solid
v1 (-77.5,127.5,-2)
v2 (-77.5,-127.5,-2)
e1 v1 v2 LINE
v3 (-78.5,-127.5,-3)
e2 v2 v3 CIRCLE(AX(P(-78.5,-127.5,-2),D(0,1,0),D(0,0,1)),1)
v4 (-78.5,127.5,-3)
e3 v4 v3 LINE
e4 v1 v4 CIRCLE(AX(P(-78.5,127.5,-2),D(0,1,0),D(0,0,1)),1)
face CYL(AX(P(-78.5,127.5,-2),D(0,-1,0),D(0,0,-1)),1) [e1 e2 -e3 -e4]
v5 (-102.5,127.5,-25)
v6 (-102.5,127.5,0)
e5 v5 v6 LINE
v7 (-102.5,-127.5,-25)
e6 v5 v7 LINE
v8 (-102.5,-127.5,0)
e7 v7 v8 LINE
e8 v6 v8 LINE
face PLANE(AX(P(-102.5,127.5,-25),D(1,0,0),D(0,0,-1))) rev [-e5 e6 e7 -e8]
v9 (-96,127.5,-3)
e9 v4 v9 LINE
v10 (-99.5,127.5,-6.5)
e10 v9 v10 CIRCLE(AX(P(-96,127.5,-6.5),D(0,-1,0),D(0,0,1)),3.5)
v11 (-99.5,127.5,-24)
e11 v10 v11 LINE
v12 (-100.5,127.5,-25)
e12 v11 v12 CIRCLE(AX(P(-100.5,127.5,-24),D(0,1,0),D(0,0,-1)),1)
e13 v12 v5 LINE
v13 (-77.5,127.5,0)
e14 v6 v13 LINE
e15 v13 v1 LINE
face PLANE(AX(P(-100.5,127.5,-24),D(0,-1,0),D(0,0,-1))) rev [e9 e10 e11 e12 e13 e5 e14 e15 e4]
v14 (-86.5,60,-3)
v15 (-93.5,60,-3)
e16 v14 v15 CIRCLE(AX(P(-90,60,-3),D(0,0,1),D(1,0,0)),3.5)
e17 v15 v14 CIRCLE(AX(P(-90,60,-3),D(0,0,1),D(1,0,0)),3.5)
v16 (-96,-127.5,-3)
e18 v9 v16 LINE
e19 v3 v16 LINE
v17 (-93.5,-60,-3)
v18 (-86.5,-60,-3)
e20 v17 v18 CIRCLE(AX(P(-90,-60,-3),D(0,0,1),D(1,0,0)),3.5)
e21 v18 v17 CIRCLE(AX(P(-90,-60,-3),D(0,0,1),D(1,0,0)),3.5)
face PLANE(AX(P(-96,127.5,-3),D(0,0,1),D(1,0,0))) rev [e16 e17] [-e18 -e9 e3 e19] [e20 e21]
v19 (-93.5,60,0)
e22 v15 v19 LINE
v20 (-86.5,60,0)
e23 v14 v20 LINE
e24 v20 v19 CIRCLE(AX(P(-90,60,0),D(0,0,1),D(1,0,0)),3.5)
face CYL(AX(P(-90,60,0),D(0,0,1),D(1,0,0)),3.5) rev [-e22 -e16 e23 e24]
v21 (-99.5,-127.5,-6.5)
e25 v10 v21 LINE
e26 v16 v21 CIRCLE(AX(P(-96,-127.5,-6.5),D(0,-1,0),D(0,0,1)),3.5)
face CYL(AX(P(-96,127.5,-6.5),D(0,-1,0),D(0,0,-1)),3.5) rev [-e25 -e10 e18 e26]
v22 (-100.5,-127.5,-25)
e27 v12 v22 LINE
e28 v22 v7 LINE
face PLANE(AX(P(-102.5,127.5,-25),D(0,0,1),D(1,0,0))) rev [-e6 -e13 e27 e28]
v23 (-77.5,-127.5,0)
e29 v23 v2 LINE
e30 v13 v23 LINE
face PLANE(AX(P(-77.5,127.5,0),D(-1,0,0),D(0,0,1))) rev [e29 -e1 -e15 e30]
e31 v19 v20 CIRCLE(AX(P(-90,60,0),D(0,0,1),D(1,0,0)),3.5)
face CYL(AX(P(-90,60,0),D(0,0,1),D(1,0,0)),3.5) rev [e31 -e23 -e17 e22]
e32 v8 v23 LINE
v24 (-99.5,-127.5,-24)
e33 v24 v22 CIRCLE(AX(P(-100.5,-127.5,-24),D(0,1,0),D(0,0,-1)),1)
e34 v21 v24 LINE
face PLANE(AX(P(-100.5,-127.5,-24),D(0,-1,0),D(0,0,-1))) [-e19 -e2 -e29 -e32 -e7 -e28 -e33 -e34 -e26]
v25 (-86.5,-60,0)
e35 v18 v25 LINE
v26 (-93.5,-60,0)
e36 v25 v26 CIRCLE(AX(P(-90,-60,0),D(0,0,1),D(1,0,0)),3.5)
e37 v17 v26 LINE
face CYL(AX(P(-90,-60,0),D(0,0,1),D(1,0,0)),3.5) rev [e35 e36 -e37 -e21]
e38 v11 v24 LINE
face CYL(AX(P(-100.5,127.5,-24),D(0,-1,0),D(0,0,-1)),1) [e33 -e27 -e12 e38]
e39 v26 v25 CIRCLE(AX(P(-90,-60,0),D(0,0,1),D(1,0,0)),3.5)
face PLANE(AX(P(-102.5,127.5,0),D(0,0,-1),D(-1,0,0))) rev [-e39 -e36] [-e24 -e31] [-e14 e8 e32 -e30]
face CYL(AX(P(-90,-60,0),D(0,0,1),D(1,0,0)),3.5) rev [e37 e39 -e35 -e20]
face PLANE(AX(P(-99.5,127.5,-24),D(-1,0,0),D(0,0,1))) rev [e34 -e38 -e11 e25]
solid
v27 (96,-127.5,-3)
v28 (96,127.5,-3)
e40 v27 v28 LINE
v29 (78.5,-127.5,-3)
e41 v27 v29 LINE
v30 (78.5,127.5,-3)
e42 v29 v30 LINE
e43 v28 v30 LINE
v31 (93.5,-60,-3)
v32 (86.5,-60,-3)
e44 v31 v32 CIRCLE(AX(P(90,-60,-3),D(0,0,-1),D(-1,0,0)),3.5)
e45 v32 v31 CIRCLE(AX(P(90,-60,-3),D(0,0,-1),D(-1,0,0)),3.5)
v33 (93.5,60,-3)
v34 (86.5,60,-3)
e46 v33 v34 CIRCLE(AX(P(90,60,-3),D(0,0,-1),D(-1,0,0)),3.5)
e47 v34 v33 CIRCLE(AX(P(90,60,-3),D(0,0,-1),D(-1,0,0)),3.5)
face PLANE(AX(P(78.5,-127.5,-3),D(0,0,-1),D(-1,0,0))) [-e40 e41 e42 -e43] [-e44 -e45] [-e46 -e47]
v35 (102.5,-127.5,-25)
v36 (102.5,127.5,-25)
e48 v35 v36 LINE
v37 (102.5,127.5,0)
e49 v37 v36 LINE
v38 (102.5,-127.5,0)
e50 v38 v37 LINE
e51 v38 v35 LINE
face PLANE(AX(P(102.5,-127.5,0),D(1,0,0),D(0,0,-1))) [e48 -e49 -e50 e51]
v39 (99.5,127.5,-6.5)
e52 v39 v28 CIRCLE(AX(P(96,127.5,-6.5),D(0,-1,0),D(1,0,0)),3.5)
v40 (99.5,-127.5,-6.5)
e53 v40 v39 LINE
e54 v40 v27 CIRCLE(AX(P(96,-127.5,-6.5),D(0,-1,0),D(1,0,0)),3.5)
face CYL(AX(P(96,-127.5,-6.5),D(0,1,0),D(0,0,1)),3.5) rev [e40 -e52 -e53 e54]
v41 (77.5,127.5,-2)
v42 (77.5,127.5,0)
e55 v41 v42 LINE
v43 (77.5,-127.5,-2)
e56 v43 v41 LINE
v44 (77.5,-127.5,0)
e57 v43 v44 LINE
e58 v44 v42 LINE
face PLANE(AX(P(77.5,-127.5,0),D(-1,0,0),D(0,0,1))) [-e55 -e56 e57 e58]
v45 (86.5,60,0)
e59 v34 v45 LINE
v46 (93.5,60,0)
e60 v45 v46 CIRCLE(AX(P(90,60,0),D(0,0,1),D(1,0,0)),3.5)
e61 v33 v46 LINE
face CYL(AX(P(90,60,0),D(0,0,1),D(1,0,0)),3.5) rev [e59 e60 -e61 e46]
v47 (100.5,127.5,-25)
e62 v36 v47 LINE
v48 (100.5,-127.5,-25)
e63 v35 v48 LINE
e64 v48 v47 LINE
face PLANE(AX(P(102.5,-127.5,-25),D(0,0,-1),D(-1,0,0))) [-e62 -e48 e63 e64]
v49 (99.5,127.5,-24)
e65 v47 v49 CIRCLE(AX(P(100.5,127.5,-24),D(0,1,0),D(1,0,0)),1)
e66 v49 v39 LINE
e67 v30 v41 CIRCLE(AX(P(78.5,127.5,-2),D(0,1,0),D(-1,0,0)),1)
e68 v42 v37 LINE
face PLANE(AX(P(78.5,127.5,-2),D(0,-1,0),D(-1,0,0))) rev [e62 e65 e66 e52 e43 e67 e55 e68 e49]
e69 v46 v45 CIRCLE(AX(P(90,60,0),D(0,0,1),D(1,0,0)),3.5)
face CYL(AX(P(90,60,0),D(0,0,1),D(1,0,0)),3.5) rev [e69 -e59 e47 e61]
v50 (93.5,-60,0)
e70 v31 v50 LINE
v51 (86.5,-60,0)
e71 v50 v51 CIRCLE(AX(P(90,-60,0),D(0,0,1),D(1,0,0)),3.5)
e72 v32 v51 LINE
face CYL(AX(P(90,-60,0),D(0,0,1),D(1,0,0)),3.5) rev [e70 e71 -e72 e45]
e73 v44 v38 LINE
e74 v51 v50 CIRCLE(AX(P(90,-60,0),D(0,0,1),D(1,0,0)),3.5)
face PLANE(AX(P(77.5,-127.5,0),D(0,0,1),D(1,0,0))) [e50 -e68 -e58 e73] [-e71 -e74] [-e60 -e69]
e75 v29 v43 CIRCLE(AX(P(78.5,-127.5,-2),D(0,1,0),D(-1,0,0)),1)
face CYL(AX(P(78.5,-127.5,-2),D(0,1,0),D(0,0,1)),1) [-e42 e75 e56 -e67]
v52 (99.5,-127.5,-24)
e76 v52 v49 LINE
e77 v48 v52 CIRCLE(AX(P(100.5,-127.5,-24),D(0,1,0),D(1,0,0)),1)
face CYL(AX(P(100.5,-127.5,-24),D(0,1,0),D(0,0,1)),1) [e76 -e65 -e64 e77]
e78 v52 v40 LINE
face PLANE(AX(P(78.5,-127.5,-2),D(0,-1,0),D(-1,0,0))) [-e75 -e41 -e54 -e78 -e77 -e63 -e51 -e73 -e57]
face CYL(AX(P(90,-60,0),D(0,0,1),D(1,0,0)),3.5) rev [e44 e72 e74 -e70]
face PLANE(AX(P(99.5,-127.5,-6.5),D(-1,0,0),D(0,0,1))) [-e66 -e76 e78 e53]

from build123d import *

# Parameters (mm, degrees)
EQUAL_ANGLE_2_5X3_1_DEPTH     = 255
EQUAL_ANGLE_2_5X3_1_2_DEPTH   = 255
M6_CLEARANCE_HOLE1_AT_2_COUNT = 2
M6_CLEARANCE_HOLE1_AT_2_PITCH = 120
M6_CLEARANCE_HOLE1_AT_3_COUNT = 2
M6_CLEARANCE_HOLE1_AT_3_PITCH = 216.333076528
M6_CLEARANCE_HOLE1_AT_4_COUNT = 2
M6_CLEARANCE_HOLE1_AT_4_PITCH = 180


with BuildPart() as part:
    # Sketch1 → Equal Angle 2.5X3(1) (new body)
    with BuildSketch(Plane(origin=(-102.5, -127.5, 0), x_dir=(0, 0, -1), z_dir=(0, 1, 0))):
        with BuildLine():
            Line((25, 0), (0, 0))
            Line((0, 0), (0, -25))
            Line((0, -25), (2, -25))
            ThreePointArc((2, -25), (2.707106781, -24.707106781), (3, -24))
            Line((3, -24), (3, -6.5))
            ThreePointArc((3, -6.5), (4.025126266, -4.025126266), (6.5, -3))
            Line((6.5, -3), (24, -3))
            ThreePointArc((24, -3), (24.707106781, -2.707106781), (25, -2))
            Line((25, -2), (25, 0))
        make_face()
    extrude(amount=EQUAL_ANGLE_2_5X3_1_DEPTH)

    # Sketch6 → M6 Clearance Hole1 (revolve, cut)
    with BuildSketch(Plane(origin=(-90, 60, 0), x_dir=(0, -1, 0), z_dir=(1, 0, 0))):
        Polygon((0, 0), (0, 22.103012167), (3.5, 20), (3.5, 0), align=None)
    m6_clearance_hole1 = revolve(axis=Axis((-90, 60, 6.35), (0, 0, -1)), mode=Mode.SUBTRACT)

    # M6 Clearance Hole1 at 2: M6 Clearance Hole1 ×2
    with Locations(*[(0, -i * M6_CLEARANCE_HOLE1_AT_2_PITCH, 0) for i in range(1, M6_CLEARANCE_HOLE1_AT_2_COUNT)]):
        add(m6_clearance_hole1, mode=Mode.SUBTRACT)


with BuildPart() as body_2:
    # Sketch1 on segment 2 (carried to segment 2) → Equal Angle 2.5X3_1 2 (new body)
    with BuildSketch(Plane(origin=(102.5, -127.5, 0), x_dir=(-1, 0, 0), z_dir=(0, 1, 0))):
        with BuildLine():
            Line((25, 0), (0, 0))
            Line((0, 0), (0, -25))
            Line((0, -25), (2, -25))
            ThreePointArc((2, -25), (2.707106781, -24.707106781), (3, -24))
            Line((3, -24), (3, -6.5))
            ThreePointArc((3, -6.5), (4.025126266, -4.025126266), (6.5, -3))
            Line((6.5, -3), (24, -3))
            ThreePointArc((24, -3), (24.707106781, -2.707106781), (25, -2))
            Line((25, -2), (25, 0))
        make_face()
    extrude(amount=EQUAL_ANGLE_2_5X3_1_2_DEPTH)

    # M6 Clearance Hole1 at 3: M6 Clearance Hole1 ×2
    with Locations(*[Vector(0.8320502943378437, -0.5547001962252293, 0) * (i * M6_CLEARANCE_HOLE1_AT_3_PITCH) for i in range(1, M6_CLEARANCE_HOLE1_AT_3_COUNT)]):
        add(m6_clearance_hole1, mode=Mode.SUBTRACT)

    # M6 Clearance Hole1 at 4: M6 Clearance Hole1 ×2
    with Locations(*[(i * M6_CLEARANCE_HOLE1_AT_4_PITCH, 0, 0) for i in range(1, M6_CLEARANCE_HOLE1_AT_4_COUNT)]):
        add(m6_clearance_hole1, mode=Mode.SUBTRACT)


solid = Compound([part.part, body_2.part])
